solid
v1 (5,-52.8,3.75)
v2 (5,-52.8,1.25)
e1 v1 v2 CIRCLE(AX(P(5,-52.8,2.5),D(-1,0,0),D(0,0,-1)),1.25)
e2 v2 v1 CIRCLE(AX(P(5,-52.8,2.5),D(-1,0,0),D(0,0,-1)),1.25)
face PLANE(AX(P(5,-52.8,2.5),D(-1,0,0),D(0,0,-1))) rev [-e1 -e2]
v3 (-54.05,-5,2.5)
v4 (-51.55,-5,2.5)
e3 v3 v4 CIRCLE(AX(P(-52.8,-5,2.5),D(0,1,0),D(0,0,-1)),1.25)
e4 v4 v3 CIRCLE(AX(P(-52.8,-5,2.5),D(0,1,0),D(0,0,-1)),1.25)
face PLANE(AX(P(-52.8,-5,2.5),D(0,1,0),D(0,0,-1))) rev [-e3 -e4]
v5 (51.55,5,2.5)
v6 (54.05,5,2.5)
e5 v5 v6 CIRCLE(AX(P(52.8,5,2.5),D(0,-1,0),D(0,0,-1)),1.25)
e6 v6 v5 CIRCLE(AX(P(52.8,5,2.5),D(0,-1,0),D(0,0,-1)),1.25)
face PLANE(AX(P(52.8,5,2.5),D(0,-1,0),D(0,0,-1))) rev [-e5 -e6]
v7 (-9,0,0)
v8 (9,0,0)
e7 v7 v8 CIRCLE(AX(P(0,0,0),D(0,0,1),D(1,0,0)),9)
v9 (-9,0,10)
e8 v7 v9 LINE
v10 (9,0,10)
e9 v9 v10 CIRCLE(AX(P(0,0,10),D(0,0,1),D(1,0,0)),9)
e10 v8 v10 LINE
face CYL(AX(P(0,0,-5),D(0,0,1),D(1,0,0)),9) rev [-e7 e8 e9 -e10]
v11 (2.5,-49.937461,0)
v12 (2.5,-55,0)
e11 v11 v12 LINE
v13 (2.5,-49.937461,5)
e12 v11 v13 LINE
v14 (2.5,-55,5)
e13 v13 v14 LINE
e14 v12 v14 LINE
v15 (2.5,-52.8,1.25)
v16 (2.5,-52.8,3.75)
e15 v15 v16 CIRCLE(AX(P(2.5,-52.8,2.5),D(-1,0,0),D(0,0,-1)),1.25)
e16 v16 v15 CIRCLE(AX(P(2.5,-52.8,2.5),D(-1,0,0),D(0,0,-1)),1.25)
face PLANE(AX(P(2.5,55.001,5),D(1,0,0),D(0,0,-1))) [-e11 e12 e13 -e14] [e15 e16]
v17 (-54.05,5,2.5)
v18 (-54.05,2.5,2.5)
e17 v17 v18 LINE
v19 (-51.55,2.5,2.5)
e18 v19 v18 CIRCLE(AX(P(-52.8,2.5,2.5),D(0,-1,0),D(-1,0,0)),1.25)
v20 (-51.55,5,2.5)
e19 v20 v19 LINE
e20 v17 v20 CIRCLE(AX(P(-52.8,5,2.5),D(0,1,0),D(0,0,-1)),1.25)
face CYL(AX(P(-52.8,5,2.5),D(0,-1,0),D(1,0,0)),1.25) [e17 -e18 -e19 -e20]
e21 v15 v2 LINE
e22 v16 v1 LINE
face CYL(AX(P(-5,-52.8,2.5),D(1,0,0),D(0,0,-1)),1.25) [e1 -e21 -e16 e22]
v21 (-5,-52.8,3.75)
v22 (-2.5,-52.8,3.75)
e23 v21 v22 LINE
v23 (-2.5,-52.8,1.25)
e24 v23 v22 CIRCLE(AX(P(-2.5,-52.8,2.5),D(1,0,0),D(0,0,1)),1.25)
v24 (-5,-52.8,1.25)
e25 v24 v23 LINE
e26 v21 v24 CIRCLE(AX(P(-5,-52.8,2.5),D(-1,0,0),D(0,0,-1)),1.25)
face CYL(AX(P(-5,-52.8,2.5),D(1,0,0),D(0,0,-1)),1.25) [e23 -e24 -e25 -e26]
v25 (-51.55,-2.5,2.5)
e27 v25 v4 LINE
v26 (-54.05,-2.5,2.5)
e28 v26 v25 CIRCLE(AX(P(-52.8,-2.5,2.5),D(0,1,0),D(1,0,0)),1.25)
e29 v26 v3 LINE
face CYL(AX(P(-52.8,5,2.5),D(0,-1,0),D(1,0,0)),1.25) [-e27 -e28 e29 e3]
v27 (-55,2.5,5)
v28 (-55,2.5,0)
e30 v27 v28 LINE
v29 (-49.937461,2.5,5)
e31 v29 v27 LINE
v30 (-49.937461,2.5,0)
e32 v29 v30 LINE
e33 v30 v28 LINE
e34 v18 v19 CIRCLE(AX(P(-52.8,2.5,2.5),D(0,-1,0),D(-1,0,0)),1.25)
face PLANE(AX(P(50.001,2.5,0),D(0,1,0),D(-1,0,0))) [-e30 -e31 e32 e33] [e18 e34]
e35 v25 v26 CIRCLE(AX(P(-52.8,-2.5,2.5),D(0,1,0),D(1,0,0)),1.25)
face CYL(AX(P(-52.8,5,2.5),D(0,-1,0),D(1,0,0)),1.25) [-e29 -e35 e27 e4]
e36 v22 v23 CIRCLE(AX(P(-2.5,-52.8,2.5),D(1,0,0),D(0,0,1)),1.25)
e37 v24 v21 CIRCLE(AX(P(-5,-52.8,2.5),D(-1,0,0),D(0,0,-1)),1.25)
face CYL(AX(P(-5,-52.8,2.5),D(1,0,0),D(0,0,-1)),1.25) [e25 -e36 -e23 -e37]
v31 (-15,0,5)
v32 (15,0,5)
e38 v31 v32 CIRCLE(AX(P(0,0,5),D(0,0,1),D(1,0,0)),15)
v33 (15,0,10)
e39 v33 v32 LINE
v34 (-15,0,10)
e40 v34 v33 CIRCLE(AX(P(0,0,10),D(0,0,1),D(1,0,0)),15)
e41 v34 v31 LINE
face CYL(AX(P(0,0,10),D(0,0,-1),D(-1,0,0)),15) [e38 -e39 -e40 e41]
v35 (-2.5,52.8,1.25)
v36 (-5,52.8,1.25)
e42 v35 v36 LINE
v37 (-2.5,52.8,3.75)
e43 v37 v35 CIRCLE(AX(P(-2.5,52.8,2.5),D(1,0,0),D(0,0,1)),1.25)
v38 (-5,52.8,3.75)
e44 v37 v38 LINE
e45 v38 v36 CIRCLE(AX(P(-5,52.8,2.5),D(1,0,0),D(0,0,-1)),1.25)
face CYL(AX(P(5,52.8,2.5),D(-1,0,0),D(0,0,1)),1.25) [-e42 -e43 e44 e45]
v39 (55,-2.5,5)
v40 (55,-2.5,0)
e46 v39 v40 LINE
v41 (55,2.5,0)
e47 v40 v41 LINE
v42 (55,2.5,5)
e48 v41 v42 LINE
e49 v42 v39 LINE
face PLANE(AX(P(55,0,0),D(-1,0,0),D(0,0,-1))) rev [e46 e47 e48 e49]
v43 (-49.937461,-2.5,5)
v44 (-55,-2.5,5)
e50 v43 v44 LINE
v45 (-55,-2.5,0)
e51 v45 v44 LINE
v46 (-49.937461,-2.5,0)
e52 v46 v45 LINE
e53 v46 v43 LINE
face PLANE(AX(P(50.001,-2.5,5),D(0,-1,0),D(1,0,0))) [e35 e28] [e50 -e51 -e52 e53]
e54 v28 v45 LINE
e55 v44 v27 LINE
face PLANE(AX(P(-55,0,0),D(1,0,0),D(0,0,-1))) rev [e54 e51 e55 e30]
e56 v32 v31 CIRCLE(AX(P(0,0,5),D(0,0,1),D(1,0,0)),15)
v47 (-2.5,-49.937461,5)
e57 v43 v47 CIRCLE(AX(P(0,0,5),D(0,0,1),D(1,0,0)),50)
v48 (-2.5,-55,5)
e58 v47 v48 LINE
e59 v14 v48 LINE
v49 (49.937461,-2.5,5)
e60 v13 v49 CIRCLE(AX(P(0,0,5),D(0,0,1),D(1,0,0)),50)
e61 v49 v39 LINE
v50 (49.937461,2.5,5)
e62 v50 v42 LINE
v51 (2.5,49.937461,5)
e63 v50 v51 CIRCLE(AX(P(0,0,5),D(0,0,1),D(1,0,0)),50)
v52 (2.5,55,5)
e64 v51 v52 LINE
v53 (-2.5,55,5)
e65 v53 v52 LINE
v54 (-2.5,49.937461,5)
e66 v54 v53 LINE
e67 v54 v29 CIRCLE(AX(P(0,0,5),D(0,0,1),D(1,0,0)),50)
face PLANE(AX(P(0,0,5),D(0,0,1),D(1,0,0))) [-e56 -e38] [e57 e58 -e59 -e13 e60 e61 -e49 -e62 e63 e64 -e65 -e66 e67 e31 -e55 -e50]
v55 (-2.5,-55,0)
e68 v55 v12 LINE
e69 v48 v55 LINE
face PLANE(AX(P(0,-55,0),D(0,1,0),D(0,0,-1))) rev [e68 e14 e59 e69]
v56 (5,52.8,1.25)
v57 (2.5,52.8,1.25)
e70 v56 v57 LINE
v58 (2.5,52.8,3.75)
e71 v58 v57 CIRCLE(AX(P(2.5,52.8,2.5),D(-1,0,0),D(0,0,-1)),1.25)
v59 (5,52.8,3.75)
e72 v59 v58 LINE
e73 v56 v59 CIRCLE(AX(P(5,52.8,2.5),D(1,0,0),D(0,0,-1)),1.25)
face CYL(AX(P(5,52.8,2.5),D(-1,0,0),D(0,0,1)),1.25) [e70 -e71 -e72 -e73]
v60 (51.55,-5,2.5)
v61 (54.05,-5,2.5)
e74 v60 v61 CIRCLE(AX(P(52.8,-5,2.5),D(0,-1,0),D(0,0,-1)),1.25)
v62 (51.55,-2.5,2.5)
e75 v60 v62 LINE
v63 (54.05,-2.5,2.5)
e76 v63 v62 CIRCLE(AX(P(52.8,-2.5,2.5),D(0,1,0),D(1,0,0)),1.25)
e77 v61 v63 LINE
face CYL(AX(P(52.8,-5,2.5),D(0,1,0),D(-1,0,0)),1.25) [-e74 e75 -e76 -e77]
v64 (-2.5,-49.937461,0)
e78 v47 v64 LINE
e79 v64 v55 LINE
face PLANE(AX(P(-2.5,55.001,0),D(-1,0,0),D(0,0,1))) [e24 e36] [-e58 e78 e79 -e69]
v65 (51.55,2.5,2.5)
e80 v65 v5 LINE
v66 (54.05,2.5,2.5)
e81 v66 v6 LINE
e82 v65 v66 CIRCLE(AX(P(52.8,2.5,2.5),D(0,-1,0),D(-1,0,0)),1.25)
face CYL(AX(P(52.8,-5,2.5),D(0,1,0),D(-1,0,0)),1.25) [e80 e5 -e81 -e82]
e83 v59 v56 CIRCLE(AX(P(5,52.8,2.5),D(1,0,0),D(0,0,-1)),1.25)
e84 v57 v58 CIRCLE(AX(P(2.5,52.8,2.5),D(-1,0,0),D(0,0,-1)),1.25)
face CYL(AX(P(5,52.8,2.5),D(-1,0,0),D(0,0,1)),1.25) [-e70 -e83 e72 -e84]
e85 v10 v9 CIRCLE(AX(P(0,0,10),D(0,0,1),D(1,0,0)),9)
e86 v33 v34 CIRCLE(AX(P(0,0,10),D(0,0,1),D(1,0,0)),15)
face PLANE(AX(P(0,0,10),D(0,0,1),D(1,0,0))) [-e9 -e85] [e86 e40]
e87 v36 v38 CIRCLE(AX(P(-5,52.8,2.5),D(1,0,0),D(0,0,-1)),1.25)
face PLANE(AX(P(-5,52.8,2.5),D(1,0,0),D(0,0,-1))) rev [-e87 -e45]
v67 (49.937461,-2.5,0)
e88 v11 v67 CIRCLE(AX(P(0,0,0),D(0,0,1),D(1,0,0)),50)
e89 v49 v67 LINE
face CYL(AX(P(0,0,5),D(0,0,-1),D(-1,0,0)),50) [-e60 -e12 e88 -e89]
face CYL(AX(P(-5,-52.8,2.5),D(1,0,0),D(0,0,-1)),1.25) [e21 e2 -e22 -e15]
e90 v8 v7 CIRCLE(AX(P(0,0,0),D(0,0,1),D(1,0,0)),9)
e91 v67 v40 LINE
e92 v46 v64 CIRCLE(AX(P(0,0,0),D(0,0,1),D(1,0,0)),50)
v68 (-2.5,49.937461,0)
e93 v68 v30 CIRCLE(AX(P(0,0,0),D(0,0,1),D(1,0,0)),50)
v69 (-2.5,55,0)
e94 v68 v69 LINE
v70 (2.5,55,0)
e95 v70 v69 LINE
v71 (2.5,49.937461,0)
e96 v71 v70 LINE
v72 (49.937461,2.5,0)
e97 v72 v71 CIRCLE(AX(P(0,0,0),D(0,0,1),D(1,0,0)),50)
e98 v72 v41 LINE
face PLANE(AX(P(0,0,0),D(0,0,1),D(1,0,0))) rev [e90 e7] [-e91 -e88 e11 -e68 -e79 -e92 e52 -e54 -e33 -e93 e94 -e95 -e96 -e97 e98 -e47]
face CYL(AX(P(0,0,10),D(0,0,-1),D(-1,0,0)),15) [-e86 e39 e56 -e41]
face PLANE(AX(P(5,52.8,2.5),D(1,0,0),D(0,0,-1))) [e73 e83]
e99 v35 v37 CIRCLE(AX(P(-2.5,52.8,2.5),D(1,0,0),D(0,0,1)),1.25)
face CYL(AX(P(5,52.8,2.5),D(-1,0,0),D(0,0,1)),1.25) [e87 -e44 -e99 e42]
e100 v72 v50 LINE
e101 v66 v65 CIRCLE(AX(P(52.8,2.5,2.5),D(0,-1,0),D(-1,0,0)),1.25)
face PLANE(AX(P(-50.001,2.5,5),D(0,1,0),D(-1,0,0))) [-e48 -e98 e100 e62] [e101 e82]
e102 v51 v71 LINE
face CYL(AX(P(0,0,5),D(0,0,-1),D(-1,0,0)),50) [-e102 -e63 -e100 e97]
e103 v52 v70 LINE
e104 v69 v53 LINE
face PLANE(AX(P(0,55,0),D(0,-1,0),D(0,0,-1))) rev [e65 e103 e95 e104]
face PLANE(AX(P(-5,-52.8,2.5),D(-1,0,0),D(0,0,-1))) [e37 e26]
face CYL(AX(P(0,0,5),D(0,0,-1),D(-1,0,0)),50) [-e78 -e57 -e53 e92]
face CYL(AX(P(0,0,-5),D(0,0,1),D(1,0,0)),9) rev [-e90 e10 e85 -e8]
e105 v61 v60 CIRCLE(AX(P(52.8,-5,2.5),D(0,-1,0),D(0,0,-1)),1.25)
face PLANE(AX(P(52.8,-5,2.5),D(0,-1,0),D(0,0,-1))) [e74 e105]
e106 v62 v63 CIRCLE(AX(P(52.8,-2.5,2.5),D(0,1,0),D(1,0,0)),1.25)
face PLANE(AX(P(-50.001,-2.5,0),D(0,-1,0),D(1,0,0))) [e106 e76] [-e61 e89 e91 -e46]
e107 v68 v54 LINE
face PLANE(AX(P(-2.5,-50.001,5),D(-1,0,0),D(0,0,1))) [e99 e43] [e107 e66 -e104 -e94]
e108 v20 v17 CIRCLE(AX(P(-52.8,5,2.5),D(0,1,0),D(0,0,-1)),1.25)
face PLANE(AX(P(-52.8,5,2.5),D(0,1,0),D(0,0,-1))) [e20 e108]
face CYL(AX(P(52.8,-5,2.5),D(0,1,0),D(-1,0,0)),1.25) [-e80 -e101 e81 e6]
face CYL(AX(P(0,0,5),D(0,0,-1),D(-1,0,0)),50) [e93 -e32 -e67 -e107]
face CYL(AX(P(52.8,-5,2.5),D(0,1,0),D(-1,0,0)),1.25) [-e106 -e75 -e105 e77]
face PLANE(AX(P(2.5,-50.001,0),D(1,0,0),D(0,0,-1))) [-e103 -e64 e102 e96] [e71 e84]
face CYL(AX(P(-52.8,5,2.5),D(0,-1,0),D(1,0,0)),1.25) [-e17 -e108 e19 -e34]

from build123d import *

# Parameters (mm, degrees)
SKETCH1_R                = 50
BOSS_EXTRUDE1_DEPTH      = 5
SKETCH2_R                = 15
BOSS_EXTRUDE2_DEPTH      = 5
SKETCH3_R                = 9
CUT_EXTRUDE1_DEPTH       = 15
BOSS_EXTRUDE3_REACH      = 118.726
BOSS_EXTRUDE3_END_RADIUS = 50
SKETCH6_R                = 1.25
BOSS_EXTRUDE4_DEPTH      = 5
CIRPATTERN3_COUNT        = 4


with BuildPart() as part:
    # Sketch1 → Boss-Extrude1 (new body)
    with BuildSketch(Plane.XY):
        Circle(SKETCH1_R)
    extrude(amount=BOSS_EXTRUDE1_DEPTH)

    # Sketch2 → Boss-Extrude2 (add)
    with BuildSketch(Plane.XY.offset(5)):
        Circle(SKETCH2_R)
    extrude(amount=BOSS_EXTRUDE2_DEPTH)

    # Sketch3 → Cut-Extrude1 (cut)
    with BuildSketch(Plane.XY.offset(10)):
        Circle(SKETCH3_R)
    extrude(amount=-CUT_EXTRUDE1_DEPTH, mode=Mode.SUBTRACT)

    # Boss-Extrude3: up to this cylinder (the profile starts outside it)
    boss_extrude3_end = Plane(origin=(0, 0, 2.5), z_dir=(0, 0, -1)) * Cylinder(BOSS_EXTRUDE3_END_RADIUS, 338.452, mode=Mode.PRIVATE)
    # Sketch4 → Boss-Extrude3 (add, up to the surface)
    with BuildSketch(Plane(origin=(0, 55, 0), x_dir=(1, 0, 0), z_dir=(0, 1, 0)), mode=Mode.PRIVATE) as boss_extrude3_sk1:
        Polygon((0, 0), (2.5, 0), (2.5, -5), (-2.5, -5), (-2.5, 0), align=None)
    boss_extrude3_tool1 = extrude(boss_extrude3_sk1.sketch, amount=-BOSS_EXTRUDE3_REACH, mode=Mode.PRIVATE) - boss_extrude3_end
    boss_extrude3 = boss_extrude3_tool1.solids().sort_by_distance((0, 55, 2.5))[0]
    add(boss_extrude3)

    # Sketch6 → Boss-Extrude4 (add, symmetric)
    with BuildSketch(Plane(origin=(0, 0, 0), x_dir=(0, 0, -1), z_dir=(1, 0, 0))):
        with Locations(Location((-2.5, 52.8, 0), (0, 0, 180))):
            Circle(SKETCH6_R)
    boss_extrude4 = extrude(amount=BOSS_EXTRUDE4_DEPTH, both=True)

    # CirPattern3: Boss-Extrude3, Boss-Extrude4 ×4 about axis
    cirpattern3_axis = Axis((0, 0, 0), (0, 0, 1))
    add([boss_extrude3.rotate(cirpattern3_axis, i * 360 / CIRPATTERN3_COUNT) for i in range(1, CIRPATTERN3_COUNT)])
    add([boss_extrude4.rotate(cirpattern3_axis, i * 360 / CIRPATTERN3_COUNT) for i in range(1, CIRPATTERN3_COUNT)])


solid = part.part
